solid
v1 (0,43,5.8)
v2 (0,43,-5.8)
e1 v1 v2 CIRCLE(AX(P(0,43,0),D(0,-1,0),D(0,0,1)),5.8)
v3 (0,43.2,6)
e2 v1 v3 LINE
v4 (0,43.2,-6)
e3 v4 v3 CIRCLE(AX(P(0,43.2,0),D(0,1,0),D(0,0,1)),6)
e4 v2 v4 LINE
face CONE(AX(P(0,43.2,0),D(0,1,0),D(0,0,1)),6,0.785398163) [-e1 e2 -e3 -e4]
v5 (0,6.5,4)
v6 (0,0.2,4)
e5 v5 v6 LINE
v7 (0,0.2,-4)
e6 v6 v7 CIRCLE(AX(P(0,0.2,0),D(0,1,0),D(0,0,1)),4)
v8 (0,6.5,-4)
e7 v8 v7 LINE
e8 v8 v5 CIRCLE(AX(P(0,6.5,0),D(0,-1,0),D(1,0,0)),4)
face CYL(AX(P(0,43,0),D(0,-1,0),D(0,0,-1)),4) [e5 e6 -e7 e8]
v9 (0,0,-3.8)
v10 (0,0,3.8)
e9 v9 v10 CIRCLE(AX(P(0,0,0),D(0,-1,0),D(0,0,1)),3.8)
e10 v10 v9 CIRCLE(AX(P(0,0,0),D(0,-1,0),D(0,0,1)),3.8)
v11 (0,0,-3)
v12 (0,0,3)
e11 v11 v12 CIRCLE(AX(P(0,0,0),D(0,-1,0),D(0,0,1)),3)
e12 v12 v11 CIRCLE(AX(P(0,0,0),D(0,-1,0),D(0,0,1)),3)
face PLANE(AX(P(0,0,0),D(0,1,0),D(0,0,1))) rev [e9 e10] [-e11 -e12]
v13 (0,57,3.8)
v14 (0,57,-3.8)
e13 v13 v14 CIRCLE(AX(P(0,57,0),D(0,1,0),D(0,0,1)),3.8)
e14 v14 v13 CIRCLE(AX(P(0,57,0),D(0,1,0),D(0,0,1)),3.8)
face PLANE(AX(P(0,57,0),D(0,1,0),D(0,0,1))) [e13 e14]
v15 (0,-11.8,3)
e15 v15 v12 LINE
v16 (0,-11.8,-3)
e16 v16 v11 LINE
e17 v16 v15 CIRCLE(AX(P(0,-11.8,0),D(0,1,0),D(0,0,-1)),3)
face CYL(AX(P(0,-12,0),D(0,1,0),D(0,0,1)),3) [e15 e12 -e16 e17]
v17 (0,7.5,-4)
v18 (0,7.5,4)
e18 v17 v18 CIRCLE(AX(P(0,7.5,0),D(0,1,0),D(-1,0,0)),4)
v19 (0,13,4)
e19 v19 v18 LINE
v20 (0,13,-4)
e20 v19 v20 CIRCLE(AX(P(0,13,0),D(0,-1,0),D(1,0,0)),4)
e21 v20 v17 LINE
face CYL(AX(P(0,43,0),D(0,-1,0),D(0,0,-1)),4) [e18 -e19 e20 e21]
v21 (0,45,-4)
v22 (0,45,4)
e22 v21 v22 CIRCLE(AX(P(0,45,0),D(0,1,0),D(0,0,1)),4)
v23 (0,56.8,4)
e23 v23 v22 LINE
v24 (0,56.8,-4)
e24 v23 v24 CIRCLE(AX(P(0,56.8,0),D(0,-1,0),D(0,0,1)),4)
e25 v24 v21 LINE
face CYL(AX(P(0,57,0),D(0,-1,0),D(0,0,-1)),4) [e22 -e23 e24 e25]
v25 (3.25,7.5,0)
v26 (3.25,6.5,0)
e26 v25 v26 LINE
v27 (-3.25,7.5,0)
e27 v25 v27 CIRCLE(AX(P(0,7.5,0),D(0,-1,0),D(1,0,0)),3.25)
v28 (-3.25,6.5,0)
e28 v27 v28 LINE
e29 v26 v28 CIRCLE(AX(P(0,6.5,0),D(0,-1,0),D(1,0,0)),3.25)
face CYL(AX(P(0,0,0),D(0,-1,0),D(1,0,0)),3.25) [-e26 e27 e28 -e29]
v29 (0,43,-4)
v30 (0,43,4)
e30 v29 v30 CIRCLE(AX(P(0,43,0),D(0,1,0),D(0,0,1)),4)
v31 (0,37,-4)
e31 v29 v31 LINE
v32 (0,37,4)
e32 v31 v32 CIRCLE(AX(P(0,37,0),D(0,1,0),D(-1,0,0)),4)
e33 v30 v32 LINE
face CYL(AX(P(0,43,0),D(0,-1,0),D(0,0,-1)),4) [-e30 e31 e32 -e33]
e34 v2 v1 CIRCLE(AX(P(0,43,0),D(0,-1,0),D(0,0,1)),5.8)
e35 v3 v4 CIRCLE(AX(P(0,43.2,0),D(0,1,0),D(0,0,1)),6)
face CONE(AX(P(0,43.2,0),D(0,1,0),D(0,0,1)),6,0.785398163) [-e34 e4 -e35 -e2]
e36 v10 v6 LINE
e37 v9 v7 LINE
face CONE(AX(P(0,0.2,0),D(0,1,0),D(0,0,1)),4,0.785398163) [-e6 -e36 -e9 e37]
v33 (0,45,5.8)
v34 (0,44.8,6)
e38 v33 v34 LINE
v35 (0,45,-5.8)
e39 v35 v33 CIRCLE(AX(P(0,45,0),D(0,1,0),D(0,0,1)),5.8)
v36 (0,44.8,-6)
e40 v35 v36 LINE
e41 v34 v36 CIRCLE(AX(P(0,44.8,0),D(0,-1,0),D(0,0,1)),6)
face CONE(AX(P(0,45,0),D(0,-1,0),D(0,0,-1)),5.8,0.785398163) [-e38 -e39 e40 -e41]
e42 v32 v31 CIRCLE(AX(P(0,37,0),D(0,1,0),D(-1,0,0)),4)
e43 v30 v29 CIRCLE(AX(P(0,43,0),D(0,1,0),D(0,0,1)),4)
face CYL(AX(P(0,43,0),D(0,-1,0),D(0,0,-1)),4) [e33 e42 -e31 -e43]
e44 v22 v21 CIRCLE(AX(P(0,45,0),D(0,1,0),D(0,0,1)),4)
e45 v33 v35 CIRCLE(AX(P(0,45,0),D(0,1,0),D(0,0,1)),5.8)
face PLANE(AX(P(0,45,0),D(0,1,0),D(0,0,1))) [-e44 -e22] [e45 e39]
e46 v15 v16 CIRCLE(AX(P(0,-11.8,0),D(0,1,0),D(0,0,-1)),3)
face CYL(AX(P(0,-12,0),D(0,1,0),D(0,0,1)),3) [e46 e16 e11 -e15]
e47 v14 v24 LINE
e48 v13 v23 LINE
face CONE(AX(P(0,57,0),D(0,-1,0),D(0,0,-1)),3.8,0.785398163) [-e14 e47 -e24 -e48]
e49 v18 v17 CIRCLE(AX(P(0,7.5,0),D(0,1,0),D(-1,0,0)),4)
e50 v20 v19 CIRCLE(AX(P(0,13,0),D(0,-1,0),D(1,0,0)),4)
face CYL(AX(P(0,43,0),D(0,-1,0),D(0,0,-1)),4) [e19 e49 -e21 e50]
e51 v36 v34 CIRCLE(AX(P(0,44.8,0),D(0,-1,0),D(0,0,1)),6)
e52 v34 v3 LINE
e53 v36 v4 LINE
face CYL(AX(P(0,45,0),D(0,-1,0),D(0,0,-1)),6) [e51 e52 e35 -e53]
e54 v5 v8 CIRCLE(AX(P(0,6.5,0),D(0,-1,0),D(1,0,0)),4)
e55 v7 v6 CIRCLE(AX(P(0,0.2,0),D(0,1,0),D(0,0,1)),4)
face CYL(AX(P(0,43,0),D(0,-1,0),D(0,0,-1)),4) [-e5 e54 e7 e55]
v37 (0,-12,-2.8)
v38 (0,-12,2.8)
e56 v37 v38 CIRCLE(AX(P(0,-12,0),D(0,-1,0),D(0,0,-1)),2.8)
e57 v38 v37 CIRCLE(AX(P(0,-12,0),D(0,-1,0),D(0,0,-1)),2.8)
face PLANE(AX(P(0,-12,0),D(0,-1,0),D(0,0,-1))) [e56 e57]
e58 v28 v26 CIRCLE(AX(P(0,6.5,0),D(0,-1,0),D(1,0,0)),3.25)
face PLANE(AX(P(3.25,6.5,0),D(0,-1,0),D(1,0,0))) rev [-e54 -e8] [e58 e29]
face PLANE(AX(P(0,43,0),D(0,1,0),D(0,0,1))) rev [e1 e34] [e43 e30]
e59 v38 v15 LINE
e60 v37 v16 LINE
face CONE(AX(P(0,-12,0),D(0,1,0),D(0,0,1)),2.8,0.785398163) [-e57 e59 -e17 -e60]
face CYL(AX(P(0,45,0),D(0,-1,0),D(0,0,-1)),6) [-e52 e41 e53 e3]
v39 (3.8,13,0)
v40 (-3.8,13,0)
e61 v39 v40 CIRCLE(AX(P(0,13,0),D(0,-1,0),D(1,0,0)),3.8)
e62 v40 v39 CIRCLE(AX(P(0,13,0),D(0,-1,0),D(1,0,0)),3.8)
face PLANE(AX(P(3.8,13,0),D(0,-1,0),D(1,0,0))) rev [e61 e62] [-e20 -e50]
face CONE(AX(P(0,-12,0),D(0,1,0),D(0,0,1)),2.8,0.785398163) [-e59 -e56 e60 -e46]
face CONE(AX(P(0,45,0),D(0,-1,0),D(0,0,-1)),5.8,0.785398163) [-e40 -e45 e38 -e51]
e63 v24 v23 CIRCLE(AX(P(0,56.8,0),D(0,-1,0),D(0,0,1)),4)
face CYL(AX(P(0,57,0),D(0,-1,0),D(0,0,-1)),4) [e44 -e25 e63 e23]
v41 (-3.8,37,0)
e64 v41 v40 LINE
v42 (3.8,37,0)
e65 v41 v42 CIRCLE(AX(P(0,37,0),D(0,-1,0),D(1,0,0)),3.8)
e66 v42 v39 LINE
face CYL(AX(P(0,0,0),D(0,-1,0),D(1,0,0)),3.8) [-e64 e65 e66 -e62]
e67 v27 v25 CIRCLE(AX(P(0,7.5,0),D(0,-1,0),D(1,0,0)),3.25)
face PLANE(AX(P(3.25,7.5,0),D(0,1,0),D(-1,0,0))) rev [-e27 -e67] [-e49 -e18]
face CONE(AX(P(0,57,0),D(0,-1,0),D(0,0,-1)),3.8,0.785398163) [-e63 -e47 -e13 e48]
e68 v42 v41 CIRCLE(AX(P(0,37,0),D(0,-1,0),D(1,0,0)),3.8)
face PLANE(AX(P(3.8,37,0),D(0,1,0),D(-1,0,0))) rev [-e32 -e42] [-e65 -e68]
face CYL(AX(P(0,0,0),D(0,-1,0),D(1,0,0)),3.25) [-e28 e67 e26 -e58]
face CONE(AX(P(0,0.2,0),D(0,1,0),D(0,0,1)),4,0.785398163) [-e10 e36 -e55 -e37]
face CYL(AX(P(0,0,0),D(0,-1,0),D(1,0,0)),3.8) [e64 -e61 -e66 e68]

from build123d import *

# Parameters (mm, degrees)
SKETCH1_R           = 4
BOSS_EXTRUDE1_DEPTH = 43
SKETCH2_R           = 6
BOSS_EXTRUDE2_DEPTH = 2
SKETCH10_R          = 4
BOSS_EXTRUDE4_DEPTH = 12
SKETCH8_W           = 4.085685727
SKETCH8_H           = 24
SKETCH8_W_2         = 3.929787065
SKETCH8_H_2         = 1
SKETCH9_R           = 3
BOSS_EXTRUDE3_DEPTH = 12
CHAMFER1_SIZE       = 0.2


with BuildPart() as part:
    # Sketch1 → Boss-Extrude1 (new body)
    with BuildSketch(Plane(origin=(0, 0, 0), x_dir=(1, 0, 0), z_dir=(0, 1, 0))):
        with Locations(Location((0, 0, 0), (0, 0, 270))):
            Circle(SKETCH1_R)
    extrude(amount=BOSS_EXTRUDE1_DEPTH)

    # Sketch2 → Boss-Extrude2 (add)
    with BuildSketch(Plane(origin=(0, 43, 0), x_dir=(1, 0, 0), z_dir=(0, 1, 0))):
        with Locations(Location((0, 0, 0), (0, 0, 270))):
            Circle(SKETCH2_R)
    extrude(amount=BOSS_EXTRUDE2_DEPTH)

    # Sketch10 → Boss-Extrude4 (add)
    with BuildSketch(Plane(origin=(0, 45, 0), x_dir=(1, 0, 0), z_dir=(0, 1, 0))):
        with Locations(Location((0, 0, 0), (0, 0, 270))):
            Circle(SKETCH10_R)
    extrude(amount=BOSS_EXTRUDE4_DEPTH)

    # Sketch8 → Cut-Revolve1 (revolve, cut)
    with BuildSketch(Plane.XY):
        with Locations((5.842842864, 25)):
            Rectangle(SKETCH8_W, SKETCH8_H)
        with Locations((5.214893532, 7)):
            Rectangle(SKETCH8_W_2, SKETCH8_H_2)
    revolve(axis=Axis((0, 0, 0), (0, 1, 0)), mode=Mode.SUBTRACT)

    # Sketch9 → Boss-Extrude3 (add)
    with BuildSketch(Plane.XZ):
        with Locations(Location((0, 0, 0), (0, 0, 90))):
            Circle(SKETCH9_R)
    extrude(amount=BOSS_EXTRUDE3_DEPTH)

    # Chamfer1
    chamfer1_edges = [part.edges().sort_by_distance(p)[0] for p in [
        (0, 57, -4),
        (0, 0, -4),
        (0, -12, -3),
        (0, 43, -6),
        (0, 45, -6),
    ]]
    chamfer(chamfer1_edges, length=CHAMFER1_SIZE)


solid = part.part
